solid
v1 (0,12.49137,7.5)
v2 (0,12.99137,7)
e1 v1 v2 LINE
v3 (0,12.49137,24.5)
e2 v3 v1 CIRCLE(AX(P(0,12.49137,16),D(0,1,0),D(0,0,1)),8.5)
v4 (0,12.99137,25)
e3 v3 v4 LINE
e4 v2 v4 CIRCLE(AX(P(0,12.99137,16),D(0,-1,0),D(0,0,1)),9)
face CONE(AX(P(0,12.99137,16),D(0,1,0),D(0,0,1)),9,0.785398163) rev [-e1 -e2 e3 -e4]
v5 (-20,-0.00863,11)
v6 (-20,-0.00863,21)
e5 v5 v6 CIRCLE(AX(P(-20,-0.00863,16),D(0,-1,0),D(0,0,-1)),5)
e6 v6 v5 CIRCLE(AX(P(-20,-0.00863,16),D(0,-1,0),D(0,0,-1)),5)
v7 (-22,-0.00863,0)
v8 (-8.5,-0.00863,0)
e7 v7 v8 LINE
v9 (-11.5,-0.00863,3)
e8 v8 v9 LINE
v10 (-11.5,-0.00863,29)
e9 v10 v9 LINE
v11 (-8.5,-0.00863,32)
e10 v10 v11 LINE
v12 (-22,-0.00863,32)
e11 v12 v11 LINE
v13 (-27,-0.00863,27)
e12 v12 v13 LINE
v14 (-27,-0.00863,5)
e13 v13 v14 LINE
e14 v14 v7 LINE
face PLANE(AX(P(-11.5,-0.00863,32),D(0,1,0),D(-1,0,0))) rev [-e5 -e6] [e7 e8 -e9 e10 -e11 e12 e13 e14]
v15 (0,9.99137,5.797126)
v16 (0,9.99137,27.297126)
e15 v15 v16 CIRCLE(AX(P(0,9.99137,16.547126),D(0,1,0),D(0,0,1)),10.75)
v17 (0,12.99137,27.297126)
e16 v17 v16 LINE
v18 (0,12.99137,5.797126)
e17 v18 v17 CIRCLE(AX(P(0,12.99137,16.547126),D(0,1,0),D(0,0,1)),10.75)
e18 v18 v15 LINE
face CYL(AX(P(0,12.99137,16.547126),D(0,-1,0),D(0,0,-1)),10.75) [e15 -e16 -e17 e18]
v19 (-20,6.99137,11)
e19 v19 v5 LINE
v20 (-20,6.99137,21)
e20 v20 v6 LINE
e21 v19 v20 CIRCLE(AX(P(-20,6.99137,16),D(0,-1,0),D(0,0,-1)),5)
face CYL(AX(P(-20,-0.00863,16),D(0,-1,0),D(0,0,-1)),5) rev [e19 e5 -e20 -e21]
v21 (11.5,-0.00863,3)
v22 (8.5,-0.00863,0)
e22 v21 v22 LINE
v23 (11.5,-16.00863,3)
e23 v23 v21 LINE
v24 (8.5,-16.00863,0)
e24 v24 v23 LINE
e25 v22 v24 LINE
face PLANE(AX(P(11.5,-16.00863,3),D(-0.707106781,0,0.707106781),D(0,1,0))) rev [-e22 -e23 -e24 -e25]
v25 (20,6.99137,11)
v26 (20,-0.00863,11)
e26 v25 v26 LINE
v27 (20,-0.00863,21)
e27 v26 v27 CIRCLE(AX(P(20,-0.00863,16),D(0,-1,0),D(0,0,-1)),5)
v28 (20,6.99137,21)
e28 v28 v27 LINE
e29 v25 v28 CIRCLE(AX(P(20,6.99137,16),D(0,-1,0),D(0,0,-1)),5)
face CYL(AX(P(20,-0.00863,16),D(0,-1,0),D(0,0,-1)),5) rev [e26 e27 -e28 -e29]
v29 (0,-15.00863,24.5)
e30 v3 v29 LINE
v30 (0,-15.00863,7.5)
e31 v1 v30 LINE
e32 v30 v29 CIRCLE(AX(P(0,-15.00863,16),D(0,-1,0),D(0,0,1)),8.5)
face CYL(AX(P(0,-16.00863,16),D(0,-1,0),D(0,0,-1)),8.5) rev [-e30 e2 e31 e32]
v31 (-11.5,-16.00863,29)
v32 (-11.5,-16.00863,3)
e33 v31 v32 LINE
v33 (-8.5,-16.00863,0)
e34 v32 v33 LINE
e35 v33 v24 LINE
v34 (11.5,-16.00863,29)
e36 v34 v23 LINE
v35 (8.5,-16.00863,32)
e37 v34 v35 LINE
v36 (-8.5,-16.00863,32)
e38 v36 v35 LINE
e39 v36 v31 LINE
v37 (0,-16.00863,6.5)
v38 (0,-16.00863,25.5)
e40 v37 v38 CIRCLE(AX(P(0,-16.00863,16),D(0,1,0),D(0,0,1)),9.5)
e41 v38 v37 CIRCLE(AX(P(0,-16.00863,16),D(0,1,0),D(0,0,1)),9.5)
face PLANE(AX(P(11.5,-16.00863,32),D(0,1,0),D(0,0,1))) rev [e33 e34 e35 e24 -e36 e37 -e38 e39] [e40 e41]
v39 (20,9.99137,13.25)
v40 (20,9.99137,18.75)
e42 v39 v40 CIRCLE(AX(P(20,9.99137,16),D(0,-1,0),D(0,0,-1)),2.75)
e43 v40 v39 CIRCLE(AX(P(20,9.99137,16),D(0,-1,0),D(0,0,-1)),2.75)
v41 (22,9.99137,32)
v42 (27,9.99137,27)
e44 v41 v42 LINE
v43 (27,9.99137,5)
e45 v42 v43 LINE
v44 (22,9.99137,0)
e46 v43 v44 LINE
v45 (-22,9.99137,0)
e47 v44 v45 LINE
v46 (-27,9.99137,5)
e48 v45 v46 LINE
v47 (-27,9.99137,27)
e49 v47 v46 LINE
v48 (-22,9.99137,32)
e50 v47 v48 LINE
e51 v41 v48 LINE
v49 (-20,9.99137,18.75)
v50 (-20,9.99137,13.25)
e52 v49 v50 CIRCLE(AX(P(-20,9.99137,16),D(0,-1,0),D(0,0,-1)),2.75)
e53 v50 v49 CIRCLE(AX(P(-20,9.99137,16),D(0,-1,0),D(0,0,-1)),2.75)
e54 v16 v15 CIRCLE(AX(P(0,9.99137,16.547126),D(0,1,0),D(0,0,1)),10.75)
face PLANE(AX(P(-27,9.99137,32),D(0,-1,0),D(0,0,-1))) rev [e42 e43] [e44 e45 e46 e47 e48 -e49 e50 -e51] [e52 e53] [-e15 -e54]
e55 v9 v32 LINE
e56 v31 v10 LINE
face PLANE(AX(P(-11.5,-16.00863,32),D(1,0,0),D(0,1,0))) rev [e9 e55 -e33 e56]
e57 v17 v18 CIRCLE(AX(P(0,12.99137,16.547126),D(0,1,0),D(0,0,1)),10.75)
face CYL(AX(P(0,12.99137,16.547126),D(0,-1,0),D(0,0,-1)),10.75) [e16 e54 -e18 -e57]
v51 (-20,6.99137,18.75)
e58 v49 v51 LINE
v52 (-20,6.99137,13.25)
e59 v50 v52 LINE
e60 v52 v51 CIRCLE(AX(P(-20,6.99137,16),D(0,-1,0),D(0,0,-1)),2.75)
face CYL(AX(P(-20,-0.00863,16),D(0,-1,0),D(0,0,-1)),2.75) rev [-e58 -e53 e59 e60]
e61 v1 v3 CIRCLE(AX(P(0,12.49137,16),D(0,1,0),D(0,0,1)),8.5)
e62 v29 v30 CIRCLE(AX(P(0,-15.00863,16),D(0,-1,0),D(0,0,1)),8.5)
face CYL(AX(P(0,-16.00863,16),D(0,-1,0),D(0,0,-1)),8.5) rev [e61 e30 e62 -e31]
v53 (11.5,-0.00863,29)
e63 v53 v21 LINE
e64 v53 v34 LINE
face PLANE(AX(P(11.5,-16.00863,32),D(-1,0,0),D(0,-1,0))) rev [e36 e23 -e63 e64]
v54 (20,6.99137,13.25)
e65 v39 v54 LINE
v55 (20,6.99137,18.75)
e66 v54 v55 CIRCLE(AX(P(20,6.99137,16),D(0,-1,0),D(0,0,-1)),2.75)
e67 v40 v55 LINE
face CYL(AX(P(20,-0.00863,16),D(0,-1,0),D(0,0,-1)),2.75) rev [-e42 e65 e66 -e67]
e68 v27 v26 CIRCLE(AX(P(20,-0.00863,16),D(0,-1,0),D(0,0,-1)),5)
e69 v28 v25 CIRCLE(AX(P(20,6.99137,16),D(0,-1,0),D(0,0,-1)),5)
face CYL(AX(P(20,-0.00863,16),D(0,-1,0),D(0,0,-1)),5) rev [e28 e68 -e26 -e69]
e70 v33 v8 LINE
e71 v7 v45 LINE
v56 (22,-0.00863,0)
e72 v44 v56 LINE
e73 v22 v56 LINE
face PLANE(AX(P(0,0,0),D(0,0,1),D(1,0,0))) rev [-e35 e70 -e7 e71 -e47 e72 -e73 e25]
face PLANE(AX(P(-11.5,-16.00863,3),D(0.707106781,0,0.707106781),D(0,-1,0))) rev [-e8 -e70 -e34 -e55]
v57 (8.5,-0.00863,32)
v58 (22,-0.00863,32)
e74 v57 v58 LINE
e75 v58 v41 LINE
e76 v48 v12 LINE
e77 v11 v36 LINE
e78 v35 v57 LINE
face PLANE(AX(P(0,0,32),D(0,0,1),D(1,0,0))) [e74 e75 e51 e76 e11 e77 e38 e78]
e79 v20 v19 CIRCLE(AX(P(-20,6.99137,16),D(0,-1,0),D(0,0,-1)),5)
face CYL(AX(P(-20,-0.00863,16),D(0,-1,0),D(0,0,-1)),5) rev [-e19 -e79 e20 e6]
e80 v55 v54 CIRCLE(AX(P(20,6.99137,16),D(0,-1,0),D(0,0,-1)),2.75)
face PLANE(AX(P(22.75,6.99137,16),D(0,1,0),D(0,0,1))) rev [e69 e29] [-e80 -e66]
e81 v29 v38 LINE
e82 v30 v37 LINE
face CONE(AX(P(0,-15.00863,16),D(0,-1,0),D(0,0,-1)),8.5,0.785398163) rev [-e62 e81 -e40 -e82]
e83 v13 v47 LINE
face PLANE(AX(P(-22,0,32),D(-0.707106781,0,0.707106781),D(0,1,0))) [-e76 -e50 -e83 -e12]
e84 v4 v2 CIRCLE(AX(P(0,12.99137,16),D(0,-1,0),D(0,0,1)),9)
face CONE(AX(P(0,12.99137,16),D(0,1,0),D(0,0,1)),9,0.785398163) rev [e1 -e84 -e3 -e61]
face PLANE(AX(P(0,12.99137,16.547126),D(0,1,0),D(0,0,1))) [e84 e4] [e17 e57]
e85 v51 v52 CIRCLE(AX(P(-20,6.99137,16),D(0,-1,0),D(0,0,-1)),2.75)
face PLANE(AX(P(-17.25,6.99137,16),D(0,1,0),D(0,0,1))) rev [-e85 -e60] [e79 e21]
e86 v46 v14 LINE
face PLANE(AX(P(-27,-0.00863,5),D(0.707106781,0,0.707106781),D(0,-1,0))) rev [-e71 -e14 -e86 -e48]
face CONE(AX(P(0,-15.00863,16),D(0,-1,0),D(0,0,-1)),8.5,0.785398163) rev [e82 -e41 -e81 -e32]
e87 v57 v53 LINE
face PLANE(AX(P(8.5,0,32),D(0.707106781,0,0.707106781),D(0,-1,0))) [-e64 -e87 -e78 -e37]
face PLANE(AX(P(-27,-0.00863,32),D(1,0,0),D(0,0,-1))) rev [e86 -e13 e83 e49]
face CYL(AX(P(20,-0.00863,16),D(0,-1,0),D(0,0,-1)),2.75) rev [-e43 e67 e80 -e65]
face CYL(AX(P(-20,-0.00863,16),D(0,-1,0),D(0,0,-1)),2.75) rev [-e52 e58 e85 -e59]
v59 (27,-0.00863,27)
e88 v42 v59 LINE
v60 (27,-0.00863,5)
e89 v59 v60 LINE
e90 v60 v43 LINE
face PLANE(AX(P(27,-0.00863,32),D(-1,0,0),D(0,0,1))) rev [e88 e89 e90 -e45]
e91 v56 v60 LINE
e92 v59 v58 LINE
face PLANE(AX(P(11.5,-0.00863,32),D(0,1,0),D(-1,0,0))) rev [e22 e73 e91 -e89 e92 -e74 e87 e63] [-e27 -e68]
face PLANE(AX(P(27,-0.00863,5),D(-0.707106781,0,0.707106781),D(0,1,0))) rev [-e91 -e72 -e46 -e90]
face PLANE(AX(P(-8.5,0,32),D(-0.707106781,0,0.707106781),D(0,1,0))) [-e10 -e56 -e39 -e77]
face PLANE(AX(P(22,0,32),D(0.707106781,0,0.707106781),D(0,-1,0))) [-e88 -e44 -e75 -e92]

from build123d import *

# Parameters (mm, degrees)
BOSS_EXTRUDE1_DEPTH = 32
CHAMFER1_SIZE       = 5
SKETCH2_R           = 10.75
BOSS_EXTRUDE2_DEPTH = 3
HOLE2_D             = 5.5
HOLE2_DEPTH         = 100
HOLE2_CBORE_D       = 10
HOLE2_CBORE_DEPTH   = 7
CHAMFER3_SIZE       = 3
HOLE3_D             = 17
CHAMFER5_SIZE       = 0.5
CHAMFER6_SIZE       = 1


with BuildPart() as part:
    # Sketch1 → Boss-Extrude1 (new body)
    with BuildSketch(Plane.XY):
        Polygon((11.5, -16.008629624), (-11.5, -16.008629624), (-11.5, -0.008629624), (-27, -0.008629624), (-27, 9.991370376), (27, 9.991370376), (27, -0.008629624), (11.5, -0.008629624), align=None)
    extrude(amount=BOSS_EXTRUDE1_DEPTH)

    # Chamfer1
    chamfer1_edges = [part.edges().sort_by_distance(p)[0] for p in [
        (-27, 4.991370376, 0),
        (27, 4.991370376, 0),
        (-27, 4.991370376, 32),
        (27, 4.991370376, 32),
    ]]
    chamfer(chamfer1_edges, length=CHAMFER1_SIZE)

    # Sketch2 → Boss-Extrude2 (add)
    with BuildSketch(Plane(origin=(0, 9.991370376, 0), x_dir=(1, 0, 0), z_dir=(0, 1, 0))):
        with Locations(Location((0, -16.547126345, 0), (0, 0, 270))):
            Circle(SKETCH2_R)
    extrude(amount=BOSS_EXTRUDE2_DEPTH)

    # Hole2
    with Locations(Plane(origin=(0, -0.008629624, 0), x_dir=(-1, 0, 0), z_dir=(0, -1, 0))):
        with Locations((-20, -16), (20, -16)):
            CounterBoreHole(HOLE2_D / 2, HOLE2_CBORE_D / 2, HOLE2_CBORE_DEPTH, depth=HOLE2_DEPTH)

    # Chamfer3
    chamfer3_edges = [part.edges().sort_by_distance(p)[0] for p in [
        (-11.5, -8.008629624, 32),
        (11.5, -8.008629624, 32),
        (11.5, -8.008629624, 0),
        (-11.5, -8.008629624, 0),
    ]]
    chamfer(chamfer3_edges, length=CHAMFER3_SIZE)

    # Hole3 (through all)
    with Locations(Plane(origin=(0, -16.008629624, 0), x_dir=(-1, 0, 0), z_dir=(0, -1, 0))):
        with Locations((0, -16)):
            Hole(HOLE3_D / 2)

    # Chamfer5
    chamfer5_edges = [part.edges().sort_by_distance(p)[0] for p in [
        (-8.5, 12.991370376, 16),
    ]]
    chamfer(chamfer5_edges, length=CHAMFER5_SIZE)

    # Chamfer6
    chamfer6_edges = [part.edges().sort_by_distance(p)[0] for p in [
        (-8.5, -16.008629624, 16),
    ]]
    chamfer(chamfer6_edges, length=CHAMFER6_SIZE)


solid = part.part
